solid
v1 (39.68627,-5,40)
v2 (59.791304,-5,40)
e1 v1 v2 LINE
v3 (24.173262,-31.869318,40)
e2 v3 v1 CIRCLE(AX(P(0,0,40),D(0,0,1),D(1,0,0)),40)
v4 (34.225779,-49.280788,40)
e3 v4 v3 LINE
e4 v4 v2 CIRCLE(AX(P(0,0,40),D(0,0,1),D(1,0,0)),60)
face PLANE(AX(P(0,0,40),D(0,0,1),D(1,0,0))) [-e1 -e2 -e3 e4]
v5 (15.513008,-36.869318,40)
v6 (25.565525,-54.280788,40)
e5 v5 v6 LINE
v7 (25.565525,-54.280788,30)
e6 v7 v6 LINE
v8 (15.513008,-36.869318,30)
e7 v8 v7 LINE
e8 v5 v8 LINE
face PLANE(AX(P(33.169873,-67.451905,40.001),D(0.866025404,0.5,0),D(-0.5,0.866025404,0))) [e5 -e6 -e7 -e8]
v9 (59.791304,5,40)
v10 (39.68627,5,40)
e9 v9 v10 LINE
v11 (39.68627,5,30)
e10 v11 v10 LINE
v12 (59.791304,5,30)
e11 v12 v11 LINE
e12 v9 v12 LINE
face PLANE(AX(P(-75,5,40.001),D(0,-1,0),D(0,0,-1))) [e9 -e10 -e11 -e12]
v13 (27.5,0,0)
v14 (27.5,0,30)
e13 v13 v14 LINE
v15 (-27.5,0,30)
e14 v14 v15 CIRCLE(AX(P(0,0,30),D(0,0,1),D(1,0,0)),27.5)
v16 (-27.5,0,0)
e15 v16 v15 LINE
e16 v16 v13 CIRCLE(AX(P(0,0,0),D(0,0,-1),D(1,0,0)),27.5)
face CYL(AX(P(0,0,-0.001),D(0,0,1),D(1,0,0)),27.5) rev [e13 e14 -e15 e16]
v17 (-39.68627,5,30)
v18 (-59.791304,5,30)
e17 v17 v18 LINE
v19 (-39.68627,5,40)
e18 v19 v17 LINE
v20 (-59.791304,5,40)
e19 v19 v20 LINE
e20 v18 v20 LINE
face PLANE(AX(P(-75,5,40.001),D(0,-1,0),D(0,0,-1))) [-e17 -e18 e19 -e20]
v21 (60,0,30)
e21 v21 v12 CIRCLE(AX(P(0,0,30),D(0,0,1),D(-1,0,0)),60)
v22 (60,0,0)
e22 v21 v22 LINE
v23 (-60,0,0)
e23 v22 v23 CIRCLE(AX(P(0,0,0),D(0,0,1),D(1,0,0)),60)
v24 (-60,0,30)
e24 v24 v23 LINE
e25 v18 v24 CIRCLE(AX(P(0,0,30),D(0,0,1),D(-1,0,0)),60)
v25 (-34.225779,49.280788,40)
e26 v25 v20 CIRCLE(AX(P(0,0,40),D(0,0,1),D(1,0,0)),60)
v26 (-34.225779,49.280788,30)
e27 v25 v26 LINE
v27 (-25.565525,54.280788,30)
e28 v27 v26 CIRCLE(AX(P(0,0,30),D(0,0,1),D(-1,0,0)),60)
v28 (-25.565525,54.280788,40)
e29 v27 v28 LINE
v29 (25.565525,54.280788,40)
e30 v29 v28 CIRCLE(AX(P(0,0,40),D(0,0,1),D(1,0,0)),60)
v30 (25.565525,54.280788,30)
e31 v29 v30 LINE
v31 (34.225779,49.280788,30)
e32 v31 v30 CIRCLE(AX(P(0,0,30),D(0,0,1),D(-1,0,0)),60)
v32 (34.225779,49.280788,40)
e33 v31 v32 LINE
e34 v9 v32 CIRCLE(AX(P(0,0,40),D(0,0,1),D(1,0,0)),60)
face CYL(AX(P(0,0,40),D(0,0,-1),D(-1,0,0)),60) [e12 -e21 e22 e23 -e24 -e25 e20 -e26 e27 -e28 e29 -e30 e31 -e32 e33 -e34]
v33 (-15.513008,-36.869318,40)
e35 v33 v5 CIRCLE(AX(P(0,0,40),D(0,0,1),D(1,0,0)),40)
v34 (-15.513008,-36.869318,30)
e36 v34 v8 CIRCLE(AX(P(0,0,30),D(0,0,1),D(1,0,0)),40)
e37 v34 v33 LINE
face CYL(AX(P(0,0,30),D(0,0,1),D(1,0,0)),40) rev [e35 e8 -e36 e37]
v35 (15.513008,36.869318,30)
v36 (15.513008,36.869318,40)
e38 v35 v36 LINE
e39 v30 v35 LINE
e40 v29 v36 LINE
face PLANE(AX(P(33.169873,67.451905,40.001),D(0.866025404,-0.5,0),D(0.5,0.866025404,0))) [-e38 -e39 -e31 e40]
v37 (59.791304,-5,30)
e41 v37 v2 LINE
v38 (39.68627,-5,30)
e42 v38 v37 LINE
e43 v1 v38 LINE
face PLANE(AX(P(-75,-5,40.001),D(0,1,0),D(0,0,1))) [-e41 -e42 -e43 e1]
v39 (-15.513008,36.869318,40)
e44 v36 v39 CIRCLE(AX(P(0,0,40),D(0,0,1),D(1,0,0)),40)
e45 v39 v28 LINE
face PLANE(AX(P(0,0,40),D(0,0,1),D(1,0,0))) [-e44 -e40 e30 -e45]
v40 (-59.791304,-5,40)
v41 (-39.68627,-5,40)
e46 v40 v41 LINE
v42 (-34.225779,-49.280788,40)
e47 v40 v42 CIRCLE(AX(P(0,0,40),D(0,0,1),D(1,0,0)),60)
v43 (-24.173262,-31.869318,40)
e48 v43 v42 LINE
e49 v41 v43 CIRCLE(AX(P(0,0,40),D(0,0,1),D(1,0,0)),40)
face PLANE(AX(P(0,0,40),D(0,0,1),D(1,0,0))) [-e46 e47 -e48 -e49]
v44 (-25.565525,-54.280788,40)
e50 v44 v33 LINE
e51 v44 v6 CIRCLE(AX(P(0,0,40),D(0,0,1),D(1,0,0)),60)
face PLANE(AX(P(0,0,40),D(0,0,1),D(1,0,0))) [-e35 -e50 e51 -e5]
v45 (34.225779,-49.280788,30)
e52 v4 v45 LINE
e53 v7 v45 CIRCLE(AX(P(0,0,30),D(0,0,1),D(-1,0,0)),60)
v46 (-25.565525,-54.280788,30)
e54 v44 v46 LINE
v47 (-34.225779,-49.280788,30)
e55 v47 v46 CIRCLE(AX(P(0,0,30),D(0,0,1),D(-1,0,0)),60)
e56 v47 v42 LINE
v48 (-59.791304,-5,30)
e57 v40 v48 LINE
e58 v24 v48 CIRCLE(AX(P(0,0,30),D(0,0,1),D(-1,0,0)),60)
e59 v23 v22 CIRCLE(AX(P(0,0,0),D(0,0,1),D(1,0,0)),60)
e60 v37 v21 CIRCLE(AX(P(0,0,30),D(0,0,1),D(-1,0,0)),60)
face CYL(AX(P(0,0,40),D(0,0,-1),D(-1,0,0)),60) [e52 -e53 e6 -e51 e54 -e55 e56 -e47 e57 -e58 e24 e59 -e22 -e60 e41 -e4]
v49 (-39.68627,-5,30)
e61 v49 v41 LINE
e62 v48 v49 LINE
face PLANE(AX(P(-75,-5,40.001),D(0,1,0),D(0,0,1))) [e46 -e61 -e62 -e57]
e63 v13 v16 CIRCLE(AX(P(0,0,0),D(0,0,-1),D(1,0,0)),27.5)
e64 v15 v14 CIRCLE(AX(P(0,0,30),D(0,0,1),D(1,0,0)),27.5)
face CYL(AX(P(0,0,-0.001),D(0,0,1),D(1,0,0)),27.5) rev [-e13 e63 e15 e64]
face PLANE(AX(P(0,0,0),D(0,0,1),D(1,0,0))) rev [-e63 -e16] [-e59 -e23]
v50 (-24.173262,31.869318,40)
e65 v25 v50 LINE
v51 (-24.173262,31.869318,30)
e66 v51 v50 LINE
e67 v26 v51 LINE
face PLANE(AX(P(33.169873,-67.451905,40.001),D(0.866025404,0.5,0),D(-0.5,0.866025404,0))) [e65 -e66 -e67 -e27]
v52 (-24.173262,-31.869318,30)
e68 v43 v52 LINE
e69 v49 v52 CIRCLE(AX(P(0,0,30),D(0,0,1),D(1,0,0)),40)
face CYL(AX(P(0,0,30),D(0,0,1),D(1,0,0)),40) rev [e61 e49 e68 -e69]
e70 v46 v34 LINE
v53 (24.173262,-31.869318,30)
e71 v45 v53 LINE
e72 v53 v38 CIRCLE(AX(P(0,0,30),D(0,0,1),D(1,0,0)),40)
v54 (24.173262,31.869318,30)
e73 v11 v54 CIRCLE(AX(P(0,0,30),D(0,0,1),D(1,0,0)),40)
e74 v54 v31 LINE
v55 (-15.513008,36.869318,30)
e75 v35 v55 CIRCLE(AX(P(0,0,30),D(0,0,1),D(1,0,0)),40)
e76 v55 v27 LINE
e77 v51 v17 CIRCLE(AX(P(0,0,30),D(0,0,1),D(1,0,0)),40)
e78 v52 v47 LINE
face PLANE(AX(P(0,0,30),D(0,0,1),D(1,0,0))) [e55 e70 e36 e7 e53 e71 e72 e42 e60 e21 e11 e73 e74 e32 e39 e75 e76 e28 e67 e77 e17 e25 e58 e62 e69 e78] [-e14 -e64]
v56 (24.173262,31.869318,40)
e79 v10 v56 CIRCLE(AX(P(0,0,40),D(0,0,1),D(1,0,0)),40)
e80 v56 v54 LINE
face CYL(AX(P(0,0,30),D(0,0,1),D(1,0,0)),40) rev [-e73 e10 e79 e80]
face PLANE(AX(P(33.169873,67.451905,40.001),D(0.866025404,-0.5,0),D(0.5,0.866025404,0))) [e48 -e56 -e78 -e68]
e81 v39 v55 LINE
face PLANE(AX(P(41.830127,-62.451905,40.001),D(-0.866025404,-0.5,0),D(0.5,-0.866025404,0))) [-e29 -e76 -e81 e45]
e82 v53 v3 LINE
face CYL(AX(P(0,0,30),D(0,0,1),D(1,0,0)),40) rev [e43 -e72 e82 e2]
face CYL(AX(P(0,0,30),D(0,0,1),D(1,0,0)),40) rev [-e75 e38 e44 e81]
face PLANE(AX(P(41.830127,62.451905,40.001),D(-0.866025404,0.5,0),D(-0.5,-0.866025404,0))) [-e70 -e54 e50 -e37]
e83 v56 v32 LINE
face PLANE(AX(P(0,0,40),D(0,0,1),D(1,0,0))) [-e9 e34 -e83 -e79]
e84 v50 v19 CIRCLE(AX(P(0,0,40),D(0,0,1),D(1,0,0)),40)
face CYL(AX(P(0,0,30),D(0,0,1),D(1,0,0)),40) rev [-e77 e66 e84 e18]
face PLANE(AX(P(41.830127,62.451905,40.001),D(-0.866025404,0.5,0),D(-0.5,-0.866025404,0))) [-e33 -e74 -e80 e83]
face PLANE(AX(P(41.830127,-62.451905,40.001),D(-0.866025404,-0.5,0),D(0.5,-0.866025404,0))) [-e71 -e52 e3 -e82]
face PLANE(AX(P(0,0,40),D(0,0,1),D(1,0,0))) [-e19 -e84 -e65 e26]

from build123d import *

# Parameters (mm, degrees)
SKETCH_1_R               = 60
EXTRUDE_1_DEPTH          = 40
SKETCH_2_R               = 40
CUT_EXTRUDE_1_DEPTH      = 10
CUT_EXTRUDE_2_REACH      = 92
SKETCH_3_R               = 27.5
SKETCH_4_W               = 150
SKETCH_4_H               = 10
CUT_EXTRUDE_3_DEPTH      = 10
PATTERN_CIRCULAR_1_COUNT = 3


with BuildPart() as part:
    # 草图1 → 凸台-拉伸1 (new body)
    with BuildSketch(Plane.XY):
        Circle(SKETCH_1_R)
    extrude(amount=EXTRUDE_1_DEPTH)

    # 草图2 → 切除-拉伸1 (cut)
    with BuildSketch(Plane.XY.offset(40)):
        Circle(SKETCH_2_R)
    extrude(amount=-CUT_EXTRUDE_1_DEPTH, mode=Mode.SUBTRACT)

    # 草图3 → 切除-拉伸2 (cut, up to next)
    with BuildSketch(Plane.XY.offset(30), mode=Mode.PRIVATE) as cut_extrude_2_sk1:
        Circle(SKETCH_3_R)
    cut_extrude_2_tool1 = extrude(cut_extrude_2_sk1.sketch, amount=-CUT_EXTRUDE_2_REACH, mode=Mode.PRIVATE) & part.part
    add(cut_extrude_2_tool1.solids().sort_by_distance((0, 0, 30))[0], mode=Mode.SUBTRACT)

    # 草图4 → 切除-拉伸3 (cut)
    with BuildSketch(Plane.XY.offset(30)):
        Rectangle(SKETCH_4_W, SKETCH_4_H)
    cut_extrude_3 = extrude(amount=CUT_EXTRUDE_3_DEPTH, mode=Mode.SUBTRACT)

    # 阵列(圆周)1: 切除-拉伸3 ×3 about axis
    pattern_circular_1_axis = Axis((0, 0, 0), (0, 0, 1))
    for i in range(1, PATTERN_CIRCULAR_1_COUNT):
        add(cut_extrude_3.rotate(pattern_circular_1_axis, i * 360 / PATTERN_CIRCULAR_1_COUNT), mode=Mode.SUBTRACT)


solid = part.part
